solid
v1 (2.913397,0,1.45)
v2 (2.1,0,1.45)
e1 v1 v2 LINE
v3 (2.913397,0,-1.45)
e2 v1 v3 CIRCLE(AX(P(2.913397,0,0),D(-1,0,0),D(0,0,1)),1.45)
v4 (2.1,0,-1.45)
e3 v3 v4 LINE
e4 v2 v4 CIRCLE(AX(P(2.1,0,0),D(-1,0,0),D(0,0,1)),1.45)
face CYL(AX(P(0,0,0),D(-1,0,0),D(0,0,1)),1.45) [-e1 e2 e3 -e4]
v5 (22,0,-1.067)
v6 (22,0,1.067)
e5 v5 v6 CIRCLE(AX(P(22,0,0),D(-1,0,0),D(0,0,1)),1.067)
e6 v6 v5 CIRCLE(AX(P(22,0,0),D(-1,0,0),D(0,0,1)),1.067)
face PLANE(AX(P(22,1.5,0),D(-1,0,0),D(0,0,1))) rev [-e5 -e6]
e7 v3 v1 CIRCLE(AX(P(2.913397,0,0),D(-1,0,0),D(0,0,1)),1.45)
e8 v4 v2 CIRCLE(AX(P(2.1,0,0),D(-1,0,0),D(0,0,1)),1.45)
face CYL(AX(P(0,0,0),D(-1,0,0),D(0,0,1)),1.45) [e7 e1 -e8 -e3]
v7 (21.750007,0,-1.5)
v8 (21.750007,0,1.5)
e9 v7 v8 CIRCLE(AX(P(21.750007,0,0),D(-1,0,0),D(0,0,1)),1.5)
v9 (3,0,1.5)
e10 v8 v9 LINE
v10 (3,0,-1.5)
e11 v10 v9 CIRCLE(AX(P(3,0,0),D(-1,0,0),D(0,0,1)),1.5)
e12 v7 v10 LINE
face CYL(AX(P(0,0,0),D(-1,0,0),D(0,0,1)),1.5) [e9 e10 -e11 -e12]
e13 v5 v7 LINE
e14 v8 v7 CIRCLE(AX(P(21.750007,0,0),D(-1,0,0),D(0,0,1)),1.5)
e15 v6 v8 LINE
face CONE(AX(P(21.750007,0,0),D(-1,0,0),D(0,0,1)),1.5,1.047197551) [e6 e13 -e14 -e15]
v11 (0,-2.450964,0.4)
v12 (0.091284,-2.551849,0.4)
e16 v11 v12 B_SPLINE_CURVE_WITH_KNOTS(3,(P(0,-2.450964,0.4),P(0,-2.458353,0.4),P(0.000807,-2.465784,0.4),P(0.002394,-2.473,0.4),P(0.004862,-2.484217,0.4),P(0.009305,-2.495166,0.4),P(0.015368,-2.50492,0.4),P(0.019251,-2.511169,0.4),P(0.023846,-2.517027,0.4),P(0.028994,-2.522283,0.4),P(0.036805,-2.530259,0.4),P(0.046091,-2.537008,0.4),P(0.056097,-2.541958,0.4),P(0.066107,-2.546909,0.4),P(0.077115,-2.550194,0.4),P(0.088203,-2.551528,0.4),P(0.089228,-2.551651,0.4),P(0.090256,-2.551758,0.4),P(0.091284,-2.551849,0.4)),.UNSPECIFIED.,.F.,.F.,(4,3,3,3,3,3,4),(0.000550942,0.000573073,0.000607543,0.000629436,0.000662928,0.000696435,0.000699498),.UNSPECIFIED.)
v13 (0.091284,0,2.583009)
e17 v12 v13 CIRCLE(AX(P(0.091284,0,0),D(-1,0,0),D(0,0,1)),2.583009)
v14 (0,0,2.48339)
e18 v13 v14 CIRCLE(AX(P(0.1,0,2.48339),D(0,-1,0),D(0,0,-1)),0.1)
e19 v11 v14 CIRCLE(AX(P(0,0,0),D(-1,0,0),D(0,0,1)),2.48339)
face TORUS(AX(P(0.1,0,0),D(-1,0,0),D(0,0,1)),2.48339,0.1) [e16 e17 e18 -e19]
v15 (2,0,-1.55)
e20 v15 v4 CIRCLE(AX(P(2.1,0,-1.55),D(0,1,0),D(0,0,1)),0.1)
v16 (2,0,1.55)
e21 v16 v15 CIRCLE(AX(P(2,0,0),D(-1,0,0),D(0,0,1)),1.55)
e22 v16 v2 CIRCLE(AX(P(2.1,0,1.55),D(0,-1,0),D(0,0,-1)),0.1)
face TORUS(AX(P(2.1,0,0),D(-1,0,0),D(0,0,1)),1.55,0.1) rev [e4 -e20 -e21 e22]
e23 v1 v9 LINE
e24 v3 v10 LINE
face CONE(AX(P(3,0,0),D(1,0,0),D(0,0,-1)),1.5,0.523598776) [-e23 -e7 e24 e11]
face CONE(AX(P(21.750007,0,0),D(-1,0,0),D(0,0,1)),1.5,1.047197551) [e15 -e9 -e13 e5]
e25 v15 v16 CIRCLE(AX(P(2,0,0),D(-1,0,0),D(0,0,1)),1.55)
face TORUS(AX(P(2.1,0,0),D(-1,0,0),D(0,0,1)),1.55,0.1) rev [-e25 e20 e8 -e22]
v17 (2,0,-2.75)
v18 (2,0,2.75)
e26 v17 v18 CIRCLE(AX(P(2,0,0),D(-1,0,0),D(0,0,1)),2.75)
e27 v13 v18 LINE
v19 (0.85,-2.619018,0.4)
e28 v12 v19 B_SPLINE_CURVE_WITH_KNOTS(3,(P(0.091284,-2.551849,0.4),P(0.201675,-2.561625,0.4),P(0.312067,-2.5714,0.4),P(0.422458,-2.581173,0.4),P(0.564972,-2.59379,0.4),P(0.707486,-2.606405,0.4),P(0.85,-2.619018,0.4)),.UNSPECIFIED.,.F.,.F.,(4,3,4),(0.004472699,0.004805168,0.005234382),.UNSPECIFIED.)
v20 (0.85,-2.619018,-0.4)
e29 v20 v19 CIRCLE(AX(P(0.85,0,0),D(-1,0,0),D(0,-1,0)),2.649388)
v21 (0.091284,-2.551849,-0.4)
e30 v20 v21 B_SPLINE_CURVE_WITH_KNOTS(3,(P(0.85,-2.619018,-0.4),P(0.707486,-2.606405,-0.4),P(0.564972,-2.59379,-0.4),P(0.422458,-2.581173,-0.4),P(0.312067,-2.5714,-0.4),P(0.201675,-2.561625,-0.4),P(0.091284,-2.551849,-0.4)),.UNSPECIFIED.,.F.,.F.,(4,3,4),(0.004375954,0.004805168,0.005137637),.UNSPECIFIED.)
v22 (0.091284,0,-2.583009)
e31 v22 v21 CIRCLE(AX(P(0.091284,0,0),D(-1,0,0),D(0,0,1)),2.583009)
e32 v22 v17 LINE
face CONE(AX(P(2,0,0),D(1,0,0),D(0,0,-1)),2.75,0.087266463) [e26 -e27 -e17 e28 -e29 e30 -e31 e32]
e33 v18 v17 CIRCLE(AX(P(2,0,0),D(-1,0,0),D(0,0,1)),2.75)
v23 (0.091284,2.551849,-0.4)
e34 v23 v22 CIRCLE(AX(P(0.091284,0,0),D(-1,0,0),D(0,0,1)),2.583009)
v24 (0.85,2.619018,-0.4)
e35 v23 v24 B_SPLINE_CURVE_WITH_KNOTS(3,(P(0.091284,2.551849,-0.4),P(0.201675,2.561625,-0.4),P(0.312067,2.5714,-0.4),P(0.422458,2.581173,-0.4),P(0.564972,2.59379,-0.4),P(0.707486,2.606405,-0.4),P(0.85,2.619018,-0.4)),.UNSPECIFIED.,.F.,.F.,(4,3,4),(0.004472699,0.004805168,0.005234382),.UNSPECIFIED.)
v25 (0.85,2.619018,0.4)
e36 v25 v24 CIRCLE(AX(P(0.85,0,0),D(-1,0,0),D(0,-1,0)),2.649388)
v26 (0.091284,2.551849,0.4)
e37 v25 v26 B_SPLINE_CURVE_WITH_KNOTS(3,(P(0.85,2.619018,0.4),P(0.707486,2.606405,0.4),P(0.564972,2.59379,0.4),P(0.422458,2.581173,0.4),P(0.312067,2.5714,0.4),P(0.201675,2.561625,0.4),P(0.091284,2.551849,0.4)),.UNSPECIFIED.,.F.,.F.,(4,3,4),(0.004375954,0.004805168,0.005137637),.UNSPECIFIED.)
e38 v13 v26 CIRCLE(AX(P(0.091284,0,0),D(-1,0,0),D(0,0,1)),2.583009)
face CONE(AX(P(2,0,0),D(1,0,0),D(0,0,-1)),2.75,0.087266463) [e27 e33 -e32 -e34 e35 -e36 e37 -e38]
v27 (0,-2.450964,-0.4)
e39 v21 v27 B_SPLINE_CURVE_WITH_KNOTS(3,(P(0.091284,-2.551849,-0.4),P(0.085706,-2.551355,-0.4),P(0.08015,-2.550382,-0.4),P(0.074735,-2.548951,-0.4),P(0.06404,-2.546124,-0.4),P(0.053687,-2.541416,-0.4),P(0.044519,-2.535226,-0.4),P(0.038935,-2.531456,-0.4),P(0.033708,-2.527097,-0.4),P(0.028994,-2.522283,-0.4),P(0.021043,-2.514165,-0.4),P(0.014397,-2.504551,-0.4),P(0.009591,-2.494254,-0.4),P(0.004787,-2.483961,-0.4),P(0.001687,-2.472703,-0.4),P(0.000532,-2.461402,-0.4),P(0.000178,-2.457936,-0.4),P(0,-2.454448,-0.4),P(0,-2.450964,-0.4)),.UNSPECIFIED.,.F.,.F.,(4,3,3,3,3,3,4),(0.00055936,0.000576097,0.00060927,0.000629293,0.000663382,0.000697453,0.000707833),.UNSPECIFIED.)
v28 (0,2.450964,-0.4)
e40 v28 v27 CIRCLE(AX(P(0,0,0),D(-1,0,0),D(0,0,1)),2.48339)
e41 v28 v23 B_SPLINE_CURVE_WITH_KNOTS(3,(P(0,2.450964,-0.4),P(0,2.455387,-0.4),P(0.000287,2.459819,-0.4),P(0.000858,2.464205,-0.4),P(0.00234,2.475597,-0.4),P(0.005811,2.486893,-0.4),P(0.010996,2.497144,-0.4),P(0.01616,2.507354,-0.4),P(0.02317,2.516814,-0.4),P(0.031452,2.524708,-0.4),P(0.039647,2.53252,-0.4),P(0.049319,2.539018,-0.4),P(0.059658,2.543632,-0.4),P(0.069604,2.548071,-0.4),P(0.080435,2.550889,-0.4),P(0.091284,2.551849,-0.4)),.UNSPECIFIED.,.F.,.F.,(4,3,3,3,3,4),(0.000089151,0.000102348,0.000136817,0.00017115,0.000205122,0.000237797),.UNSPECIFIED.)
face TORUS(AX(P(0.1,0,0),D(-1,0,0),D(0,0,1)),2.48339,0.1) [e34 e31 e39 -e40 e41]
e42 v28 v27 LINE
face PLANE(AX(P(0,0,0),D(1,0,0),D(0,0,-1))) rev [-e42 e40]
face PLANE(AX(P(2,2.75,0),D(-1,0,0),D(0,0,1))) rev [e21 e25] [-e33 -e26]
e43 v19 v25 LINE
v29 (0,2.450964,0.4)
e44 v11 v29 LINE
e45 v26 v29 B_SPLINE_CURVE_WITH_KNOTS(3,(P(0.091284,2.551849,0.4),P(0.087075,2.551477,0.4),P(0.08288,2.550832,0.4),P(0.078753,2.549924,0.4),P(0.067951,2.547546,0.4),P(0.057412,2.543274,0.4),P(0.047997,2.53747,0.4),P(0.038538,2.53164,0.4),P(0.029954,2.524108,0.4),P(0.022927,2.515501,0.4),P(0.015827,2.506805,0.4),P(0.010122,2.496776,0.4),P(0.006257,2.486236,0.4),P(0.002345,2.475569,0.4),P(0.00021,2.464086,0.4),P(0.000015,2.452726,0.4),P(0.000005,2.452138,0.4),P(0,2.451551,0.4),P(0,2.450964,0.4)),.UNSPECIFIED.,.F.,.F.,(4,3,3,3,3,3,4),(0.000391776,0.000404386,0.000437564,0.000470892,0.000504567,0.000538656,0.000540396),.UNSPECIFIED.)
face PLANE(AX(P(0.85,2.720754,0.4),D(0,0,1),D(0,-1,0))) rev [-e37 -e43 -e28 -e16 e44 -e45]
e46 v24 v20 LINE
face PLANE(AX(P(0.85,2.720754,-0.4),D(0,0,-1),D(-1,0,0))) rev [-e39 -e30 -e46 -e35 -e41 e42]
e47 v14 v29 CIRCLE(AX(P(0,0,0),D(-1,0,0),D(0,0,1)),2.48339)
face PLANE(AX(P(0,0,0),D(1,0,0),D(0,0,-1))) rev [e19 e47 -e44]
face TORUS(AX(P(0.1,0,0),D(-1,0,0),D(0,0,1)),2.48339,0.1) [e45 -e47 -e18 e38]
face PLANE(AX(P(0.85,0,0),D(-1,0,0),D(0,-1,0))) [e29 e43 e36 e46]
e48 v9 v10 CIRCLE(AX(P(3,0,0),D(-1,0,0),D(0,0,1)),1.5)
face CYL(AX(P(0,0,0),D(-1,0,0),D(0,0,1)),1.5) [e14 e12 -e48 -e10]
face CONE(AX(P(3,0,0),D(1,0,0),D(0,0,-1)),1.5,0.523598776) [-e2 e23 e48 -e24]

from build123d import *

# Parameters (mm, degrees)
CUT_EXTRUDE1_DEPTH = 0.85


with BuildPart() as part:
    # Sketch1 → Base-Revolve (revolve)
    with BuildSketch(Plane.XY, mode=Mode.PRIVATE) as base_revolve_sk:
        with BuildLine():
            Line((0, 0), (0, 2.483389556))
            ThreePointArc((0, 2.483389556), (0.026272266, 2.550948576), (0.091284426, 2.583009025))
            Line((0.091284426, 2.583009025), (2, 2.75))
            Line((2, 2.75), (2, 1.55))
            ThreePointArc((2, 1.55), (2.029289322, 1.479289322), (2.1, 1.45))
            Line((2.1, 1.45), (2.91339746, 1.45))
            Line((2.91339746, 1.45), (3, 1.5))
            Line((3, 1.5), (22, 1.5))
            Line((22, 1.5), (22, 0))
            Line((22, 0), (0, 0))
        make_face()
    revolve(base_revolve_sk.sketch.rotate(Axis((0, 0, 0), (1, 0, 0)), 90), axis=Axis((0, 0, 0), (1, 0, 0)))

    # Sketch2 → Cut-Extrude1 (cut)
    with BuildSketch(Plane.ZY):
        with BuildLine():
            Line((0.4, 2.720753572), (0.4, -2.720753572))
            ThreePointArc((0.4, -2.720753572), (0, -2.75), (-0.4, -2.720753572))
            Line((-0.4, -2.720753572), (-0.4, 2.720753572))
            ThreePointArc((-0.4, 2.720753572), (0, 2.75), (0.4, 2.720753572))
        make_face()
    extrude(amount=-CUT_EXTRUDE1_DEPTH, mode=Mode.SUBTRACT)

    # Sketch3 → Cut-Revolve1 (revolve, cut)
    with BuildSketch(Plane(origin=(0, 0, 0), x_dir=(1, 0, 0), z_dir=(0, 1, 0)), mode=Mode.PRIVATE) as cut_revolve1_sk:
        Polygon((21.750007333, 1.5), (22.249992667, 1.5), (22, 1.067), align=None)
    revolve(cut_revolve1_sk.sketch.rotate(Axis((0, 0, 0), (1, 0, 0)), 180), axis=Axis((0, 0, 0), (1, 0, 0)), mode=Mode.SUBTRACT)


solid = part.part
